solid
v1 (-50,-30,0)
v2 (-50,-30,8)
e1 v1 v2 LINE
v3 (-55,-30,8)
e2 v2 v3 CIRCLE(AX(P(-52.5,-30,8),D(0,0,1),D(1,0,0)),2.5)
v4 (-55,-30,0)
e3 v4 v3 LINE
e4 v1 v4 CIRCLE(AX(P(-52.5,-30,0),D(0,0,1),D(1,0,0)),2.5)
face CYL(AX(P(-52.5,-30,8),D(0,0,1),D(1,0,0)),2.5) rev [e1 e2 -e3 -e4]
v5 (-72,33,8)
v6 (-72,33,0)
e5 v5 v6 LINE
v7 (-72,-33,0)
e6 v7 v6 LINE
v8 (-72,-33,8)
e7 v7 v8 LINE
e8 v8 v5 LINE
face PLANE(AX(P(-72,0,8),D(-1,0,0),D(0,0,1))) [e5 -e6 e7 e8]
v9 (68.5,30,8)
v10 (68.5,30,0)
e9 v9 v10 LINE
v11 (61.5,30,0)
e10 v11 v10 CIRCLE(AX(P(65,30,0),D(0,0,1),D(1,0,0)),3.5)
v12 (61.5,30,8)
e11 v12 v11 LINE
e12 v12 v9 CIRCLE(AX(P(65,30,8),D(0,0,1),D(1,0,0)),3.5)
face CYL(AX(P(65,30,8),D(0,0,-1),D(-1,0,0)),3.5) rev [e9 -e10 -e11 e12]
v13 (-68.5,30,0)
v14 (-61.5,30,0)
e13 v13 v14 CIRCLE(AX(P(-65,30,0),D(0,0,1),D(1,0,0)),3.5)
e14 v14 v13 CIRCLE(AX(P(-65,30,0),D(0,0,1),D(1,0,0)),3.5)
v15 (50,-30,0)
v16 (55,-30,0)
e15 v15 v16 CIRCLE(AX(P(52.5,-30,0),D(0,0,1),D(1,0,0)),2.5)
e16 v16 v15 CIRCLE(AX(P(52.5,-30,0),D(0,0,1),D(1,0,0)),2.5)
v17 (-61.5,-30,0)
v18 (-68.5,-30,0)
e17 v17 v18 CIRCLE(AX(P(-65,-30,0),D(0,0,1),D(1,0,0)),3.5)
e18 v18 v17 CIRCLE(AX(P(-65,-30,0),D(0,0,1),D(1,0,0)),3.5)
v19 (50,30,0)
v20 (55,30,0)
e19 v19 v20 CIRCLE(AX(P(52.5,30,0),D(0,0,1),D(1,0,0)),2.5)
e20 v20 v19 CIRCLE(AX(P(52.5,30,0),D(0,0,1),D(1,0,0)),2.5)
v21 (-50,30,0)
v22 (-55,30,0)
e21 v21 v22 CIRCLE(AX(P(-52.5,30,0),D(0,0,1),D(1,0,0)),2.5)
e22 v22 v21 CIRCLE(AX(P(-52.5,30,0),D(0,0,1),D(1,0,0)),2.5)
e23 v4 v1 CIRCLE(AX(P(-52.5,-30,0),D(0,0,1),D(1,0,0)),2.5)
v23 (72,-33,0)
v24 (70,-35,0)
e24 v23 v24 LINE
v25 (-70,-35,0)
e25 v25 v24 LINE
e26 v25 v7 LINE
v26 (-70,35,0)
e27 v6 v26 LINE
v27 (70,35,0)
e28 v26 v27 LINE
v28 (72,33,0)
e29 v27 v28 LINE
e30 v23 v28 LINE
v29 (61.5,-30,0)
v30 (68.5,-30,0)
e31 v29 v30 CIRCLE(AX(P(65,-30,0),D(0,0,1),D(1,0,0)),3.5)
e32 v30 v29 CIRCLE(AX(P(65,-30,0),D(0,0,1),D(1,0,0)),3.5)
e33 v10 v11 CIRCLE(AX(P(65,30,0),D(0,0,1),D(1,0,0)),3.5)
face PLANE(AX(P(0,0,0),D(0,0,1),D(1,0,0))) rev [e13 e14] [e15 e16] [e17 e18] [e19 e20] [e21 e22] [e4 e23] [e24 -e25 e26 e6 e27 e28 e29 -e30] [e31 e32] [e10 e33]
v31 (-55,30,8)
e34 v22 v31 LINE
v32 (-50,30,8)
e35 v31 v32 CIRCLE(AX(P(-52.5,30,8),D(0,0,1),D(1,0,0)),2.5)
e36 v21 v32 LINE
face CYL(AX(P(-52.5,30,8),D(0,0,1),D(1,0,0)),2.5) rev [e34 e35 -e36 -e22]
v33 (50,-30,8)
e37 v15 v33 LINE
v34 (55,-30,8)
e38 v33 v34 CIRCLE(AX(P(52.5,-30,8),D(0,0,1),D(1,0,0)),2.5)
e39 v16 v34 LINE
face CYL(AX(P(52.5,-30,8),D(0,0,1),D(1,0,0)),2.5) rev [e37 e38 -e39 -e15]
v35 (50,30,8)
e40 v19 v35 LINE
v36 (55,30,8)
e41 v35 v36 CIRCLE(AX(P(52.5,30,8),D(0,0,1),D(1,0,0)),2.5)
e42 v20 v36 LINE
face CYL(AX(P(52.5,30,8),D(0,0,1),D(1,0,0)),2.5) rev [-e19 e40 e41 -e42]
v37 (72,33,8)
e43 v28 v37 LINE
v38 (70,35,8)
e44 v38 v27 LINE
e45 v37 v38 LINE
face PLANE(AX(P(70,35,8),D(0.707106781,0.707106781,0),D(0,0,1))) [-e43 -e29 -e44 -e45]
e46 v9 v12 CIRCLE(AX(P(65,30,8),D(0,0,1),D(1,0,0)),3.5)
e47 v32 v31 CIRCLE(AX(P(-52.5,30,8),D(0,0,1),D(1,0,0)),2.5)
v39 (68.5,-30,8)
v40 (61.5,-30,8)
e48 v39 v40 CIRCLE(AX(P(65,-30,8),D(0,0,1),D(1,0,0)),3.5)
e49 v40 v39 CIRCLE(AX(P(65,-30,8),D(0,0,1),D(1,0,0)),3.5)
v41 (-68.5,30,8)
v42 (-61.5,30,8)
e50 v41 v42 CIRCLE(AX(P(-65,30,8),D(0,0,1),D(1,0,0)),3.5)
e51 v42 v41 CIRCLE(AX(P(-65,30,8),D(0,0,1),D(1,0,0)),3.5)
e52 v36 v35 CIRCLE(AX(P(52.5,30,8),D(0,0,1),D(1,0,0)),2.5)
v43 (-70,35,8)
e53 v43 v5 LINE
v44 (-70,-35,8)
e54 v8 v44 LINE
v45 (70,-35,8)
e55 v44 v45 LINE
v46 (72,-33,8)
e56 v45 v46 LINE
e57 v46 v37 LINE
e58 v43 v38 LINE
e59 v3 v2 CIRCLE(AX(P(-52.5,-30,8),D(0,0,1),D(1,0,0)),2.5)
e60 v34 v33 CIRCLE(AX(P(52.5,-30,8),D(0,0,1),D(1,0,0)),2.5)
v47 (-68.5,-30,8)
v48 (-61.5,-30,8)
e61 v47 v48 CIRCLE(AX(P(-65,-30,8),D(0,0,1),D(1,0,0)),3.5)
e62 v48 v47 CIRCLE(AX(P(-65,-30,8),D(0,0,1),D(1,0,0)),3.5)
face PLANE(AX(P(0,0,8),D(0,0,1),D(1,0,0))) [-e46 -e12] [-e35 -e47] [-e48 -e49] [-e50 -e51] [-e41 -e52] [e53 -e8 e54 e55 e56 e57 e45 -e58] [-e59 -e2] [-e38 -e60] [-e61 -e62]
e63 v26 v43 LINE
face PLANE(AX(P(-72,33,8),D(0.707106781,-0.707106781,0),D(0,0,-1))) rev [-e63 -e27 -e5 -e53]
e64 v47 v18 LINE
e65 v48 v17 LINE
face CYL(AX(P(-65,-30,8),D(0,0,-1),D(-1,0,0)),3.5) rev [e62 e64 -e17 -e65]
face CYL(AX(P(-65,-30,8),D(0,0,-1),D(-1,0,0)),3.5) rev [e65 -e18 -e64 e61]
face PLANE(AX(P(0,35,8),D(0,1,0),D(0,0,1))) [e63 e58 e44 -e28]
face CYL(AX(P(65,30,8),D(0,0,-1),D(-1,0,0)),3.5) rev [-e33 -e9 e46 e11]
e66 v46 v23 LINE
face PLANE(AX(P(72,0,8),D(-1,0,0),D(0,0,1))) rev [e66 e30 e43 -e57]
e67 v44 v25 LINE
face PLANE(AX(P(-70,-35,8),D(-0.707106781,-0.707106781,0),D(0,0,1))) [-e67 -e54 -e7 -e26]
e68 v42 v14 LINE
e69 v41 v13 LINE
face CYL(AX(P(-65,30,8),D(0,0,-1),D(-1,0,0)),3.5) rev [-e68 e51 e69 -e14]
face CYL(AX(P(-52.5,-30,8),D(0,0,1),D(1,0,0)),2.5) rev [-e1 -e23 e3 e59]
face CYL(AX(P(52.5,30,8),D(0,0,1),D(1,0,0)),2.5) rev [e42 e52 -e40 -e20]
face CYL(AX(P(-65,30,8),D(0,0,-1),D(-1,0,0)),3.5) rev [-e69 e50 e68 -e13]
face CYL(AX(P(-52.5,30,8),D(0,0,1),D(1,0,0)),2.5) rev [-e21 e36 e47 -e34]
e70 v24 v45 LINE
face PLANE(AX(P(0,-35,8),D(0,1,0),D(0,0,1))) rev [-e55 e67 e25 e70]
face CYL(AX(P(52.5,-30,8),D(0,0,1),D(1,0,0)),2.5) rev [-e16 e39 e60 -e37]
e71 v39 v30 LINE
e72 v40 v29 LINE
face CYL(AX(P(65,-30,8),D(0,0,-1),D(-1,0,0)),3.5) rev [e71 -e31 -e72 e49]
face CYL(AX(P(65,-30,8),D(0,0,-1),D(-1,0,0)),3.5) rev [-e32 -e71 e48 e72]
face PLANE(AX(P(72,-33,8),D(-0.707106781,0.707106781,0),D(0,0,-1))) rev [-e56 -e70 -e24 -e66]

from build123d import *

# Parameters (mm, degrees)
SKETCH1_W           = 144
SKETCH1_H           = 70
SKETCH1_R           = 3.5
BOSS_EXTRUDE1_DEPTH = 8
CHAMFER1_SIZE       = 2
M6_TAPPED_HOLE1_D   = 5


with BuildPart() as part:
    # Sketch1 → Boss-Extrude1 (new body)
    with BuildSketch(Plane.XY):
        Rectangle(SKETCH1_W, SKETCH1_H)
        with Locations((65, 30)):
            Circle(SKETCH1_R, mode=Mode.SUBTRACT)
        with Locations((65, -30)):
            Circle(SKETCH1_R, mode=Mode.SUBTRACT)
        with Locations((-65, -30)):
            Circle(SKETCH1_R, mode=Mode.SUBTRACT)
        with Locations((-65, 30)):
            Circle(SKETCH1_R, mode=Mode.SUBTRACT)
    extrude(amount=BOSS_EXTRUDE1_DEPTH)

    # Chamfer1
    chamfer1_edges = [part.edges().sort_by_distance(p)[0] for p in [
        (-72, -35, 4),
        (-72, 35, 4),
        (72, 35, 4),
        (72, -35, 4),
    ]]
    chamfer(chamfer1_edges, length=CHAMFER1_SIZE)

    # M6 Tapped Hole1 (through all)
    with Locations(Plane.XY.offset(8)):
        with Locations((-52.5, 30), (-52.5, -30), (52.5, -30), (52.5, 30)):
            Hole(M6_TAPPED_HOLE1_D / 2)


solid = part.part
